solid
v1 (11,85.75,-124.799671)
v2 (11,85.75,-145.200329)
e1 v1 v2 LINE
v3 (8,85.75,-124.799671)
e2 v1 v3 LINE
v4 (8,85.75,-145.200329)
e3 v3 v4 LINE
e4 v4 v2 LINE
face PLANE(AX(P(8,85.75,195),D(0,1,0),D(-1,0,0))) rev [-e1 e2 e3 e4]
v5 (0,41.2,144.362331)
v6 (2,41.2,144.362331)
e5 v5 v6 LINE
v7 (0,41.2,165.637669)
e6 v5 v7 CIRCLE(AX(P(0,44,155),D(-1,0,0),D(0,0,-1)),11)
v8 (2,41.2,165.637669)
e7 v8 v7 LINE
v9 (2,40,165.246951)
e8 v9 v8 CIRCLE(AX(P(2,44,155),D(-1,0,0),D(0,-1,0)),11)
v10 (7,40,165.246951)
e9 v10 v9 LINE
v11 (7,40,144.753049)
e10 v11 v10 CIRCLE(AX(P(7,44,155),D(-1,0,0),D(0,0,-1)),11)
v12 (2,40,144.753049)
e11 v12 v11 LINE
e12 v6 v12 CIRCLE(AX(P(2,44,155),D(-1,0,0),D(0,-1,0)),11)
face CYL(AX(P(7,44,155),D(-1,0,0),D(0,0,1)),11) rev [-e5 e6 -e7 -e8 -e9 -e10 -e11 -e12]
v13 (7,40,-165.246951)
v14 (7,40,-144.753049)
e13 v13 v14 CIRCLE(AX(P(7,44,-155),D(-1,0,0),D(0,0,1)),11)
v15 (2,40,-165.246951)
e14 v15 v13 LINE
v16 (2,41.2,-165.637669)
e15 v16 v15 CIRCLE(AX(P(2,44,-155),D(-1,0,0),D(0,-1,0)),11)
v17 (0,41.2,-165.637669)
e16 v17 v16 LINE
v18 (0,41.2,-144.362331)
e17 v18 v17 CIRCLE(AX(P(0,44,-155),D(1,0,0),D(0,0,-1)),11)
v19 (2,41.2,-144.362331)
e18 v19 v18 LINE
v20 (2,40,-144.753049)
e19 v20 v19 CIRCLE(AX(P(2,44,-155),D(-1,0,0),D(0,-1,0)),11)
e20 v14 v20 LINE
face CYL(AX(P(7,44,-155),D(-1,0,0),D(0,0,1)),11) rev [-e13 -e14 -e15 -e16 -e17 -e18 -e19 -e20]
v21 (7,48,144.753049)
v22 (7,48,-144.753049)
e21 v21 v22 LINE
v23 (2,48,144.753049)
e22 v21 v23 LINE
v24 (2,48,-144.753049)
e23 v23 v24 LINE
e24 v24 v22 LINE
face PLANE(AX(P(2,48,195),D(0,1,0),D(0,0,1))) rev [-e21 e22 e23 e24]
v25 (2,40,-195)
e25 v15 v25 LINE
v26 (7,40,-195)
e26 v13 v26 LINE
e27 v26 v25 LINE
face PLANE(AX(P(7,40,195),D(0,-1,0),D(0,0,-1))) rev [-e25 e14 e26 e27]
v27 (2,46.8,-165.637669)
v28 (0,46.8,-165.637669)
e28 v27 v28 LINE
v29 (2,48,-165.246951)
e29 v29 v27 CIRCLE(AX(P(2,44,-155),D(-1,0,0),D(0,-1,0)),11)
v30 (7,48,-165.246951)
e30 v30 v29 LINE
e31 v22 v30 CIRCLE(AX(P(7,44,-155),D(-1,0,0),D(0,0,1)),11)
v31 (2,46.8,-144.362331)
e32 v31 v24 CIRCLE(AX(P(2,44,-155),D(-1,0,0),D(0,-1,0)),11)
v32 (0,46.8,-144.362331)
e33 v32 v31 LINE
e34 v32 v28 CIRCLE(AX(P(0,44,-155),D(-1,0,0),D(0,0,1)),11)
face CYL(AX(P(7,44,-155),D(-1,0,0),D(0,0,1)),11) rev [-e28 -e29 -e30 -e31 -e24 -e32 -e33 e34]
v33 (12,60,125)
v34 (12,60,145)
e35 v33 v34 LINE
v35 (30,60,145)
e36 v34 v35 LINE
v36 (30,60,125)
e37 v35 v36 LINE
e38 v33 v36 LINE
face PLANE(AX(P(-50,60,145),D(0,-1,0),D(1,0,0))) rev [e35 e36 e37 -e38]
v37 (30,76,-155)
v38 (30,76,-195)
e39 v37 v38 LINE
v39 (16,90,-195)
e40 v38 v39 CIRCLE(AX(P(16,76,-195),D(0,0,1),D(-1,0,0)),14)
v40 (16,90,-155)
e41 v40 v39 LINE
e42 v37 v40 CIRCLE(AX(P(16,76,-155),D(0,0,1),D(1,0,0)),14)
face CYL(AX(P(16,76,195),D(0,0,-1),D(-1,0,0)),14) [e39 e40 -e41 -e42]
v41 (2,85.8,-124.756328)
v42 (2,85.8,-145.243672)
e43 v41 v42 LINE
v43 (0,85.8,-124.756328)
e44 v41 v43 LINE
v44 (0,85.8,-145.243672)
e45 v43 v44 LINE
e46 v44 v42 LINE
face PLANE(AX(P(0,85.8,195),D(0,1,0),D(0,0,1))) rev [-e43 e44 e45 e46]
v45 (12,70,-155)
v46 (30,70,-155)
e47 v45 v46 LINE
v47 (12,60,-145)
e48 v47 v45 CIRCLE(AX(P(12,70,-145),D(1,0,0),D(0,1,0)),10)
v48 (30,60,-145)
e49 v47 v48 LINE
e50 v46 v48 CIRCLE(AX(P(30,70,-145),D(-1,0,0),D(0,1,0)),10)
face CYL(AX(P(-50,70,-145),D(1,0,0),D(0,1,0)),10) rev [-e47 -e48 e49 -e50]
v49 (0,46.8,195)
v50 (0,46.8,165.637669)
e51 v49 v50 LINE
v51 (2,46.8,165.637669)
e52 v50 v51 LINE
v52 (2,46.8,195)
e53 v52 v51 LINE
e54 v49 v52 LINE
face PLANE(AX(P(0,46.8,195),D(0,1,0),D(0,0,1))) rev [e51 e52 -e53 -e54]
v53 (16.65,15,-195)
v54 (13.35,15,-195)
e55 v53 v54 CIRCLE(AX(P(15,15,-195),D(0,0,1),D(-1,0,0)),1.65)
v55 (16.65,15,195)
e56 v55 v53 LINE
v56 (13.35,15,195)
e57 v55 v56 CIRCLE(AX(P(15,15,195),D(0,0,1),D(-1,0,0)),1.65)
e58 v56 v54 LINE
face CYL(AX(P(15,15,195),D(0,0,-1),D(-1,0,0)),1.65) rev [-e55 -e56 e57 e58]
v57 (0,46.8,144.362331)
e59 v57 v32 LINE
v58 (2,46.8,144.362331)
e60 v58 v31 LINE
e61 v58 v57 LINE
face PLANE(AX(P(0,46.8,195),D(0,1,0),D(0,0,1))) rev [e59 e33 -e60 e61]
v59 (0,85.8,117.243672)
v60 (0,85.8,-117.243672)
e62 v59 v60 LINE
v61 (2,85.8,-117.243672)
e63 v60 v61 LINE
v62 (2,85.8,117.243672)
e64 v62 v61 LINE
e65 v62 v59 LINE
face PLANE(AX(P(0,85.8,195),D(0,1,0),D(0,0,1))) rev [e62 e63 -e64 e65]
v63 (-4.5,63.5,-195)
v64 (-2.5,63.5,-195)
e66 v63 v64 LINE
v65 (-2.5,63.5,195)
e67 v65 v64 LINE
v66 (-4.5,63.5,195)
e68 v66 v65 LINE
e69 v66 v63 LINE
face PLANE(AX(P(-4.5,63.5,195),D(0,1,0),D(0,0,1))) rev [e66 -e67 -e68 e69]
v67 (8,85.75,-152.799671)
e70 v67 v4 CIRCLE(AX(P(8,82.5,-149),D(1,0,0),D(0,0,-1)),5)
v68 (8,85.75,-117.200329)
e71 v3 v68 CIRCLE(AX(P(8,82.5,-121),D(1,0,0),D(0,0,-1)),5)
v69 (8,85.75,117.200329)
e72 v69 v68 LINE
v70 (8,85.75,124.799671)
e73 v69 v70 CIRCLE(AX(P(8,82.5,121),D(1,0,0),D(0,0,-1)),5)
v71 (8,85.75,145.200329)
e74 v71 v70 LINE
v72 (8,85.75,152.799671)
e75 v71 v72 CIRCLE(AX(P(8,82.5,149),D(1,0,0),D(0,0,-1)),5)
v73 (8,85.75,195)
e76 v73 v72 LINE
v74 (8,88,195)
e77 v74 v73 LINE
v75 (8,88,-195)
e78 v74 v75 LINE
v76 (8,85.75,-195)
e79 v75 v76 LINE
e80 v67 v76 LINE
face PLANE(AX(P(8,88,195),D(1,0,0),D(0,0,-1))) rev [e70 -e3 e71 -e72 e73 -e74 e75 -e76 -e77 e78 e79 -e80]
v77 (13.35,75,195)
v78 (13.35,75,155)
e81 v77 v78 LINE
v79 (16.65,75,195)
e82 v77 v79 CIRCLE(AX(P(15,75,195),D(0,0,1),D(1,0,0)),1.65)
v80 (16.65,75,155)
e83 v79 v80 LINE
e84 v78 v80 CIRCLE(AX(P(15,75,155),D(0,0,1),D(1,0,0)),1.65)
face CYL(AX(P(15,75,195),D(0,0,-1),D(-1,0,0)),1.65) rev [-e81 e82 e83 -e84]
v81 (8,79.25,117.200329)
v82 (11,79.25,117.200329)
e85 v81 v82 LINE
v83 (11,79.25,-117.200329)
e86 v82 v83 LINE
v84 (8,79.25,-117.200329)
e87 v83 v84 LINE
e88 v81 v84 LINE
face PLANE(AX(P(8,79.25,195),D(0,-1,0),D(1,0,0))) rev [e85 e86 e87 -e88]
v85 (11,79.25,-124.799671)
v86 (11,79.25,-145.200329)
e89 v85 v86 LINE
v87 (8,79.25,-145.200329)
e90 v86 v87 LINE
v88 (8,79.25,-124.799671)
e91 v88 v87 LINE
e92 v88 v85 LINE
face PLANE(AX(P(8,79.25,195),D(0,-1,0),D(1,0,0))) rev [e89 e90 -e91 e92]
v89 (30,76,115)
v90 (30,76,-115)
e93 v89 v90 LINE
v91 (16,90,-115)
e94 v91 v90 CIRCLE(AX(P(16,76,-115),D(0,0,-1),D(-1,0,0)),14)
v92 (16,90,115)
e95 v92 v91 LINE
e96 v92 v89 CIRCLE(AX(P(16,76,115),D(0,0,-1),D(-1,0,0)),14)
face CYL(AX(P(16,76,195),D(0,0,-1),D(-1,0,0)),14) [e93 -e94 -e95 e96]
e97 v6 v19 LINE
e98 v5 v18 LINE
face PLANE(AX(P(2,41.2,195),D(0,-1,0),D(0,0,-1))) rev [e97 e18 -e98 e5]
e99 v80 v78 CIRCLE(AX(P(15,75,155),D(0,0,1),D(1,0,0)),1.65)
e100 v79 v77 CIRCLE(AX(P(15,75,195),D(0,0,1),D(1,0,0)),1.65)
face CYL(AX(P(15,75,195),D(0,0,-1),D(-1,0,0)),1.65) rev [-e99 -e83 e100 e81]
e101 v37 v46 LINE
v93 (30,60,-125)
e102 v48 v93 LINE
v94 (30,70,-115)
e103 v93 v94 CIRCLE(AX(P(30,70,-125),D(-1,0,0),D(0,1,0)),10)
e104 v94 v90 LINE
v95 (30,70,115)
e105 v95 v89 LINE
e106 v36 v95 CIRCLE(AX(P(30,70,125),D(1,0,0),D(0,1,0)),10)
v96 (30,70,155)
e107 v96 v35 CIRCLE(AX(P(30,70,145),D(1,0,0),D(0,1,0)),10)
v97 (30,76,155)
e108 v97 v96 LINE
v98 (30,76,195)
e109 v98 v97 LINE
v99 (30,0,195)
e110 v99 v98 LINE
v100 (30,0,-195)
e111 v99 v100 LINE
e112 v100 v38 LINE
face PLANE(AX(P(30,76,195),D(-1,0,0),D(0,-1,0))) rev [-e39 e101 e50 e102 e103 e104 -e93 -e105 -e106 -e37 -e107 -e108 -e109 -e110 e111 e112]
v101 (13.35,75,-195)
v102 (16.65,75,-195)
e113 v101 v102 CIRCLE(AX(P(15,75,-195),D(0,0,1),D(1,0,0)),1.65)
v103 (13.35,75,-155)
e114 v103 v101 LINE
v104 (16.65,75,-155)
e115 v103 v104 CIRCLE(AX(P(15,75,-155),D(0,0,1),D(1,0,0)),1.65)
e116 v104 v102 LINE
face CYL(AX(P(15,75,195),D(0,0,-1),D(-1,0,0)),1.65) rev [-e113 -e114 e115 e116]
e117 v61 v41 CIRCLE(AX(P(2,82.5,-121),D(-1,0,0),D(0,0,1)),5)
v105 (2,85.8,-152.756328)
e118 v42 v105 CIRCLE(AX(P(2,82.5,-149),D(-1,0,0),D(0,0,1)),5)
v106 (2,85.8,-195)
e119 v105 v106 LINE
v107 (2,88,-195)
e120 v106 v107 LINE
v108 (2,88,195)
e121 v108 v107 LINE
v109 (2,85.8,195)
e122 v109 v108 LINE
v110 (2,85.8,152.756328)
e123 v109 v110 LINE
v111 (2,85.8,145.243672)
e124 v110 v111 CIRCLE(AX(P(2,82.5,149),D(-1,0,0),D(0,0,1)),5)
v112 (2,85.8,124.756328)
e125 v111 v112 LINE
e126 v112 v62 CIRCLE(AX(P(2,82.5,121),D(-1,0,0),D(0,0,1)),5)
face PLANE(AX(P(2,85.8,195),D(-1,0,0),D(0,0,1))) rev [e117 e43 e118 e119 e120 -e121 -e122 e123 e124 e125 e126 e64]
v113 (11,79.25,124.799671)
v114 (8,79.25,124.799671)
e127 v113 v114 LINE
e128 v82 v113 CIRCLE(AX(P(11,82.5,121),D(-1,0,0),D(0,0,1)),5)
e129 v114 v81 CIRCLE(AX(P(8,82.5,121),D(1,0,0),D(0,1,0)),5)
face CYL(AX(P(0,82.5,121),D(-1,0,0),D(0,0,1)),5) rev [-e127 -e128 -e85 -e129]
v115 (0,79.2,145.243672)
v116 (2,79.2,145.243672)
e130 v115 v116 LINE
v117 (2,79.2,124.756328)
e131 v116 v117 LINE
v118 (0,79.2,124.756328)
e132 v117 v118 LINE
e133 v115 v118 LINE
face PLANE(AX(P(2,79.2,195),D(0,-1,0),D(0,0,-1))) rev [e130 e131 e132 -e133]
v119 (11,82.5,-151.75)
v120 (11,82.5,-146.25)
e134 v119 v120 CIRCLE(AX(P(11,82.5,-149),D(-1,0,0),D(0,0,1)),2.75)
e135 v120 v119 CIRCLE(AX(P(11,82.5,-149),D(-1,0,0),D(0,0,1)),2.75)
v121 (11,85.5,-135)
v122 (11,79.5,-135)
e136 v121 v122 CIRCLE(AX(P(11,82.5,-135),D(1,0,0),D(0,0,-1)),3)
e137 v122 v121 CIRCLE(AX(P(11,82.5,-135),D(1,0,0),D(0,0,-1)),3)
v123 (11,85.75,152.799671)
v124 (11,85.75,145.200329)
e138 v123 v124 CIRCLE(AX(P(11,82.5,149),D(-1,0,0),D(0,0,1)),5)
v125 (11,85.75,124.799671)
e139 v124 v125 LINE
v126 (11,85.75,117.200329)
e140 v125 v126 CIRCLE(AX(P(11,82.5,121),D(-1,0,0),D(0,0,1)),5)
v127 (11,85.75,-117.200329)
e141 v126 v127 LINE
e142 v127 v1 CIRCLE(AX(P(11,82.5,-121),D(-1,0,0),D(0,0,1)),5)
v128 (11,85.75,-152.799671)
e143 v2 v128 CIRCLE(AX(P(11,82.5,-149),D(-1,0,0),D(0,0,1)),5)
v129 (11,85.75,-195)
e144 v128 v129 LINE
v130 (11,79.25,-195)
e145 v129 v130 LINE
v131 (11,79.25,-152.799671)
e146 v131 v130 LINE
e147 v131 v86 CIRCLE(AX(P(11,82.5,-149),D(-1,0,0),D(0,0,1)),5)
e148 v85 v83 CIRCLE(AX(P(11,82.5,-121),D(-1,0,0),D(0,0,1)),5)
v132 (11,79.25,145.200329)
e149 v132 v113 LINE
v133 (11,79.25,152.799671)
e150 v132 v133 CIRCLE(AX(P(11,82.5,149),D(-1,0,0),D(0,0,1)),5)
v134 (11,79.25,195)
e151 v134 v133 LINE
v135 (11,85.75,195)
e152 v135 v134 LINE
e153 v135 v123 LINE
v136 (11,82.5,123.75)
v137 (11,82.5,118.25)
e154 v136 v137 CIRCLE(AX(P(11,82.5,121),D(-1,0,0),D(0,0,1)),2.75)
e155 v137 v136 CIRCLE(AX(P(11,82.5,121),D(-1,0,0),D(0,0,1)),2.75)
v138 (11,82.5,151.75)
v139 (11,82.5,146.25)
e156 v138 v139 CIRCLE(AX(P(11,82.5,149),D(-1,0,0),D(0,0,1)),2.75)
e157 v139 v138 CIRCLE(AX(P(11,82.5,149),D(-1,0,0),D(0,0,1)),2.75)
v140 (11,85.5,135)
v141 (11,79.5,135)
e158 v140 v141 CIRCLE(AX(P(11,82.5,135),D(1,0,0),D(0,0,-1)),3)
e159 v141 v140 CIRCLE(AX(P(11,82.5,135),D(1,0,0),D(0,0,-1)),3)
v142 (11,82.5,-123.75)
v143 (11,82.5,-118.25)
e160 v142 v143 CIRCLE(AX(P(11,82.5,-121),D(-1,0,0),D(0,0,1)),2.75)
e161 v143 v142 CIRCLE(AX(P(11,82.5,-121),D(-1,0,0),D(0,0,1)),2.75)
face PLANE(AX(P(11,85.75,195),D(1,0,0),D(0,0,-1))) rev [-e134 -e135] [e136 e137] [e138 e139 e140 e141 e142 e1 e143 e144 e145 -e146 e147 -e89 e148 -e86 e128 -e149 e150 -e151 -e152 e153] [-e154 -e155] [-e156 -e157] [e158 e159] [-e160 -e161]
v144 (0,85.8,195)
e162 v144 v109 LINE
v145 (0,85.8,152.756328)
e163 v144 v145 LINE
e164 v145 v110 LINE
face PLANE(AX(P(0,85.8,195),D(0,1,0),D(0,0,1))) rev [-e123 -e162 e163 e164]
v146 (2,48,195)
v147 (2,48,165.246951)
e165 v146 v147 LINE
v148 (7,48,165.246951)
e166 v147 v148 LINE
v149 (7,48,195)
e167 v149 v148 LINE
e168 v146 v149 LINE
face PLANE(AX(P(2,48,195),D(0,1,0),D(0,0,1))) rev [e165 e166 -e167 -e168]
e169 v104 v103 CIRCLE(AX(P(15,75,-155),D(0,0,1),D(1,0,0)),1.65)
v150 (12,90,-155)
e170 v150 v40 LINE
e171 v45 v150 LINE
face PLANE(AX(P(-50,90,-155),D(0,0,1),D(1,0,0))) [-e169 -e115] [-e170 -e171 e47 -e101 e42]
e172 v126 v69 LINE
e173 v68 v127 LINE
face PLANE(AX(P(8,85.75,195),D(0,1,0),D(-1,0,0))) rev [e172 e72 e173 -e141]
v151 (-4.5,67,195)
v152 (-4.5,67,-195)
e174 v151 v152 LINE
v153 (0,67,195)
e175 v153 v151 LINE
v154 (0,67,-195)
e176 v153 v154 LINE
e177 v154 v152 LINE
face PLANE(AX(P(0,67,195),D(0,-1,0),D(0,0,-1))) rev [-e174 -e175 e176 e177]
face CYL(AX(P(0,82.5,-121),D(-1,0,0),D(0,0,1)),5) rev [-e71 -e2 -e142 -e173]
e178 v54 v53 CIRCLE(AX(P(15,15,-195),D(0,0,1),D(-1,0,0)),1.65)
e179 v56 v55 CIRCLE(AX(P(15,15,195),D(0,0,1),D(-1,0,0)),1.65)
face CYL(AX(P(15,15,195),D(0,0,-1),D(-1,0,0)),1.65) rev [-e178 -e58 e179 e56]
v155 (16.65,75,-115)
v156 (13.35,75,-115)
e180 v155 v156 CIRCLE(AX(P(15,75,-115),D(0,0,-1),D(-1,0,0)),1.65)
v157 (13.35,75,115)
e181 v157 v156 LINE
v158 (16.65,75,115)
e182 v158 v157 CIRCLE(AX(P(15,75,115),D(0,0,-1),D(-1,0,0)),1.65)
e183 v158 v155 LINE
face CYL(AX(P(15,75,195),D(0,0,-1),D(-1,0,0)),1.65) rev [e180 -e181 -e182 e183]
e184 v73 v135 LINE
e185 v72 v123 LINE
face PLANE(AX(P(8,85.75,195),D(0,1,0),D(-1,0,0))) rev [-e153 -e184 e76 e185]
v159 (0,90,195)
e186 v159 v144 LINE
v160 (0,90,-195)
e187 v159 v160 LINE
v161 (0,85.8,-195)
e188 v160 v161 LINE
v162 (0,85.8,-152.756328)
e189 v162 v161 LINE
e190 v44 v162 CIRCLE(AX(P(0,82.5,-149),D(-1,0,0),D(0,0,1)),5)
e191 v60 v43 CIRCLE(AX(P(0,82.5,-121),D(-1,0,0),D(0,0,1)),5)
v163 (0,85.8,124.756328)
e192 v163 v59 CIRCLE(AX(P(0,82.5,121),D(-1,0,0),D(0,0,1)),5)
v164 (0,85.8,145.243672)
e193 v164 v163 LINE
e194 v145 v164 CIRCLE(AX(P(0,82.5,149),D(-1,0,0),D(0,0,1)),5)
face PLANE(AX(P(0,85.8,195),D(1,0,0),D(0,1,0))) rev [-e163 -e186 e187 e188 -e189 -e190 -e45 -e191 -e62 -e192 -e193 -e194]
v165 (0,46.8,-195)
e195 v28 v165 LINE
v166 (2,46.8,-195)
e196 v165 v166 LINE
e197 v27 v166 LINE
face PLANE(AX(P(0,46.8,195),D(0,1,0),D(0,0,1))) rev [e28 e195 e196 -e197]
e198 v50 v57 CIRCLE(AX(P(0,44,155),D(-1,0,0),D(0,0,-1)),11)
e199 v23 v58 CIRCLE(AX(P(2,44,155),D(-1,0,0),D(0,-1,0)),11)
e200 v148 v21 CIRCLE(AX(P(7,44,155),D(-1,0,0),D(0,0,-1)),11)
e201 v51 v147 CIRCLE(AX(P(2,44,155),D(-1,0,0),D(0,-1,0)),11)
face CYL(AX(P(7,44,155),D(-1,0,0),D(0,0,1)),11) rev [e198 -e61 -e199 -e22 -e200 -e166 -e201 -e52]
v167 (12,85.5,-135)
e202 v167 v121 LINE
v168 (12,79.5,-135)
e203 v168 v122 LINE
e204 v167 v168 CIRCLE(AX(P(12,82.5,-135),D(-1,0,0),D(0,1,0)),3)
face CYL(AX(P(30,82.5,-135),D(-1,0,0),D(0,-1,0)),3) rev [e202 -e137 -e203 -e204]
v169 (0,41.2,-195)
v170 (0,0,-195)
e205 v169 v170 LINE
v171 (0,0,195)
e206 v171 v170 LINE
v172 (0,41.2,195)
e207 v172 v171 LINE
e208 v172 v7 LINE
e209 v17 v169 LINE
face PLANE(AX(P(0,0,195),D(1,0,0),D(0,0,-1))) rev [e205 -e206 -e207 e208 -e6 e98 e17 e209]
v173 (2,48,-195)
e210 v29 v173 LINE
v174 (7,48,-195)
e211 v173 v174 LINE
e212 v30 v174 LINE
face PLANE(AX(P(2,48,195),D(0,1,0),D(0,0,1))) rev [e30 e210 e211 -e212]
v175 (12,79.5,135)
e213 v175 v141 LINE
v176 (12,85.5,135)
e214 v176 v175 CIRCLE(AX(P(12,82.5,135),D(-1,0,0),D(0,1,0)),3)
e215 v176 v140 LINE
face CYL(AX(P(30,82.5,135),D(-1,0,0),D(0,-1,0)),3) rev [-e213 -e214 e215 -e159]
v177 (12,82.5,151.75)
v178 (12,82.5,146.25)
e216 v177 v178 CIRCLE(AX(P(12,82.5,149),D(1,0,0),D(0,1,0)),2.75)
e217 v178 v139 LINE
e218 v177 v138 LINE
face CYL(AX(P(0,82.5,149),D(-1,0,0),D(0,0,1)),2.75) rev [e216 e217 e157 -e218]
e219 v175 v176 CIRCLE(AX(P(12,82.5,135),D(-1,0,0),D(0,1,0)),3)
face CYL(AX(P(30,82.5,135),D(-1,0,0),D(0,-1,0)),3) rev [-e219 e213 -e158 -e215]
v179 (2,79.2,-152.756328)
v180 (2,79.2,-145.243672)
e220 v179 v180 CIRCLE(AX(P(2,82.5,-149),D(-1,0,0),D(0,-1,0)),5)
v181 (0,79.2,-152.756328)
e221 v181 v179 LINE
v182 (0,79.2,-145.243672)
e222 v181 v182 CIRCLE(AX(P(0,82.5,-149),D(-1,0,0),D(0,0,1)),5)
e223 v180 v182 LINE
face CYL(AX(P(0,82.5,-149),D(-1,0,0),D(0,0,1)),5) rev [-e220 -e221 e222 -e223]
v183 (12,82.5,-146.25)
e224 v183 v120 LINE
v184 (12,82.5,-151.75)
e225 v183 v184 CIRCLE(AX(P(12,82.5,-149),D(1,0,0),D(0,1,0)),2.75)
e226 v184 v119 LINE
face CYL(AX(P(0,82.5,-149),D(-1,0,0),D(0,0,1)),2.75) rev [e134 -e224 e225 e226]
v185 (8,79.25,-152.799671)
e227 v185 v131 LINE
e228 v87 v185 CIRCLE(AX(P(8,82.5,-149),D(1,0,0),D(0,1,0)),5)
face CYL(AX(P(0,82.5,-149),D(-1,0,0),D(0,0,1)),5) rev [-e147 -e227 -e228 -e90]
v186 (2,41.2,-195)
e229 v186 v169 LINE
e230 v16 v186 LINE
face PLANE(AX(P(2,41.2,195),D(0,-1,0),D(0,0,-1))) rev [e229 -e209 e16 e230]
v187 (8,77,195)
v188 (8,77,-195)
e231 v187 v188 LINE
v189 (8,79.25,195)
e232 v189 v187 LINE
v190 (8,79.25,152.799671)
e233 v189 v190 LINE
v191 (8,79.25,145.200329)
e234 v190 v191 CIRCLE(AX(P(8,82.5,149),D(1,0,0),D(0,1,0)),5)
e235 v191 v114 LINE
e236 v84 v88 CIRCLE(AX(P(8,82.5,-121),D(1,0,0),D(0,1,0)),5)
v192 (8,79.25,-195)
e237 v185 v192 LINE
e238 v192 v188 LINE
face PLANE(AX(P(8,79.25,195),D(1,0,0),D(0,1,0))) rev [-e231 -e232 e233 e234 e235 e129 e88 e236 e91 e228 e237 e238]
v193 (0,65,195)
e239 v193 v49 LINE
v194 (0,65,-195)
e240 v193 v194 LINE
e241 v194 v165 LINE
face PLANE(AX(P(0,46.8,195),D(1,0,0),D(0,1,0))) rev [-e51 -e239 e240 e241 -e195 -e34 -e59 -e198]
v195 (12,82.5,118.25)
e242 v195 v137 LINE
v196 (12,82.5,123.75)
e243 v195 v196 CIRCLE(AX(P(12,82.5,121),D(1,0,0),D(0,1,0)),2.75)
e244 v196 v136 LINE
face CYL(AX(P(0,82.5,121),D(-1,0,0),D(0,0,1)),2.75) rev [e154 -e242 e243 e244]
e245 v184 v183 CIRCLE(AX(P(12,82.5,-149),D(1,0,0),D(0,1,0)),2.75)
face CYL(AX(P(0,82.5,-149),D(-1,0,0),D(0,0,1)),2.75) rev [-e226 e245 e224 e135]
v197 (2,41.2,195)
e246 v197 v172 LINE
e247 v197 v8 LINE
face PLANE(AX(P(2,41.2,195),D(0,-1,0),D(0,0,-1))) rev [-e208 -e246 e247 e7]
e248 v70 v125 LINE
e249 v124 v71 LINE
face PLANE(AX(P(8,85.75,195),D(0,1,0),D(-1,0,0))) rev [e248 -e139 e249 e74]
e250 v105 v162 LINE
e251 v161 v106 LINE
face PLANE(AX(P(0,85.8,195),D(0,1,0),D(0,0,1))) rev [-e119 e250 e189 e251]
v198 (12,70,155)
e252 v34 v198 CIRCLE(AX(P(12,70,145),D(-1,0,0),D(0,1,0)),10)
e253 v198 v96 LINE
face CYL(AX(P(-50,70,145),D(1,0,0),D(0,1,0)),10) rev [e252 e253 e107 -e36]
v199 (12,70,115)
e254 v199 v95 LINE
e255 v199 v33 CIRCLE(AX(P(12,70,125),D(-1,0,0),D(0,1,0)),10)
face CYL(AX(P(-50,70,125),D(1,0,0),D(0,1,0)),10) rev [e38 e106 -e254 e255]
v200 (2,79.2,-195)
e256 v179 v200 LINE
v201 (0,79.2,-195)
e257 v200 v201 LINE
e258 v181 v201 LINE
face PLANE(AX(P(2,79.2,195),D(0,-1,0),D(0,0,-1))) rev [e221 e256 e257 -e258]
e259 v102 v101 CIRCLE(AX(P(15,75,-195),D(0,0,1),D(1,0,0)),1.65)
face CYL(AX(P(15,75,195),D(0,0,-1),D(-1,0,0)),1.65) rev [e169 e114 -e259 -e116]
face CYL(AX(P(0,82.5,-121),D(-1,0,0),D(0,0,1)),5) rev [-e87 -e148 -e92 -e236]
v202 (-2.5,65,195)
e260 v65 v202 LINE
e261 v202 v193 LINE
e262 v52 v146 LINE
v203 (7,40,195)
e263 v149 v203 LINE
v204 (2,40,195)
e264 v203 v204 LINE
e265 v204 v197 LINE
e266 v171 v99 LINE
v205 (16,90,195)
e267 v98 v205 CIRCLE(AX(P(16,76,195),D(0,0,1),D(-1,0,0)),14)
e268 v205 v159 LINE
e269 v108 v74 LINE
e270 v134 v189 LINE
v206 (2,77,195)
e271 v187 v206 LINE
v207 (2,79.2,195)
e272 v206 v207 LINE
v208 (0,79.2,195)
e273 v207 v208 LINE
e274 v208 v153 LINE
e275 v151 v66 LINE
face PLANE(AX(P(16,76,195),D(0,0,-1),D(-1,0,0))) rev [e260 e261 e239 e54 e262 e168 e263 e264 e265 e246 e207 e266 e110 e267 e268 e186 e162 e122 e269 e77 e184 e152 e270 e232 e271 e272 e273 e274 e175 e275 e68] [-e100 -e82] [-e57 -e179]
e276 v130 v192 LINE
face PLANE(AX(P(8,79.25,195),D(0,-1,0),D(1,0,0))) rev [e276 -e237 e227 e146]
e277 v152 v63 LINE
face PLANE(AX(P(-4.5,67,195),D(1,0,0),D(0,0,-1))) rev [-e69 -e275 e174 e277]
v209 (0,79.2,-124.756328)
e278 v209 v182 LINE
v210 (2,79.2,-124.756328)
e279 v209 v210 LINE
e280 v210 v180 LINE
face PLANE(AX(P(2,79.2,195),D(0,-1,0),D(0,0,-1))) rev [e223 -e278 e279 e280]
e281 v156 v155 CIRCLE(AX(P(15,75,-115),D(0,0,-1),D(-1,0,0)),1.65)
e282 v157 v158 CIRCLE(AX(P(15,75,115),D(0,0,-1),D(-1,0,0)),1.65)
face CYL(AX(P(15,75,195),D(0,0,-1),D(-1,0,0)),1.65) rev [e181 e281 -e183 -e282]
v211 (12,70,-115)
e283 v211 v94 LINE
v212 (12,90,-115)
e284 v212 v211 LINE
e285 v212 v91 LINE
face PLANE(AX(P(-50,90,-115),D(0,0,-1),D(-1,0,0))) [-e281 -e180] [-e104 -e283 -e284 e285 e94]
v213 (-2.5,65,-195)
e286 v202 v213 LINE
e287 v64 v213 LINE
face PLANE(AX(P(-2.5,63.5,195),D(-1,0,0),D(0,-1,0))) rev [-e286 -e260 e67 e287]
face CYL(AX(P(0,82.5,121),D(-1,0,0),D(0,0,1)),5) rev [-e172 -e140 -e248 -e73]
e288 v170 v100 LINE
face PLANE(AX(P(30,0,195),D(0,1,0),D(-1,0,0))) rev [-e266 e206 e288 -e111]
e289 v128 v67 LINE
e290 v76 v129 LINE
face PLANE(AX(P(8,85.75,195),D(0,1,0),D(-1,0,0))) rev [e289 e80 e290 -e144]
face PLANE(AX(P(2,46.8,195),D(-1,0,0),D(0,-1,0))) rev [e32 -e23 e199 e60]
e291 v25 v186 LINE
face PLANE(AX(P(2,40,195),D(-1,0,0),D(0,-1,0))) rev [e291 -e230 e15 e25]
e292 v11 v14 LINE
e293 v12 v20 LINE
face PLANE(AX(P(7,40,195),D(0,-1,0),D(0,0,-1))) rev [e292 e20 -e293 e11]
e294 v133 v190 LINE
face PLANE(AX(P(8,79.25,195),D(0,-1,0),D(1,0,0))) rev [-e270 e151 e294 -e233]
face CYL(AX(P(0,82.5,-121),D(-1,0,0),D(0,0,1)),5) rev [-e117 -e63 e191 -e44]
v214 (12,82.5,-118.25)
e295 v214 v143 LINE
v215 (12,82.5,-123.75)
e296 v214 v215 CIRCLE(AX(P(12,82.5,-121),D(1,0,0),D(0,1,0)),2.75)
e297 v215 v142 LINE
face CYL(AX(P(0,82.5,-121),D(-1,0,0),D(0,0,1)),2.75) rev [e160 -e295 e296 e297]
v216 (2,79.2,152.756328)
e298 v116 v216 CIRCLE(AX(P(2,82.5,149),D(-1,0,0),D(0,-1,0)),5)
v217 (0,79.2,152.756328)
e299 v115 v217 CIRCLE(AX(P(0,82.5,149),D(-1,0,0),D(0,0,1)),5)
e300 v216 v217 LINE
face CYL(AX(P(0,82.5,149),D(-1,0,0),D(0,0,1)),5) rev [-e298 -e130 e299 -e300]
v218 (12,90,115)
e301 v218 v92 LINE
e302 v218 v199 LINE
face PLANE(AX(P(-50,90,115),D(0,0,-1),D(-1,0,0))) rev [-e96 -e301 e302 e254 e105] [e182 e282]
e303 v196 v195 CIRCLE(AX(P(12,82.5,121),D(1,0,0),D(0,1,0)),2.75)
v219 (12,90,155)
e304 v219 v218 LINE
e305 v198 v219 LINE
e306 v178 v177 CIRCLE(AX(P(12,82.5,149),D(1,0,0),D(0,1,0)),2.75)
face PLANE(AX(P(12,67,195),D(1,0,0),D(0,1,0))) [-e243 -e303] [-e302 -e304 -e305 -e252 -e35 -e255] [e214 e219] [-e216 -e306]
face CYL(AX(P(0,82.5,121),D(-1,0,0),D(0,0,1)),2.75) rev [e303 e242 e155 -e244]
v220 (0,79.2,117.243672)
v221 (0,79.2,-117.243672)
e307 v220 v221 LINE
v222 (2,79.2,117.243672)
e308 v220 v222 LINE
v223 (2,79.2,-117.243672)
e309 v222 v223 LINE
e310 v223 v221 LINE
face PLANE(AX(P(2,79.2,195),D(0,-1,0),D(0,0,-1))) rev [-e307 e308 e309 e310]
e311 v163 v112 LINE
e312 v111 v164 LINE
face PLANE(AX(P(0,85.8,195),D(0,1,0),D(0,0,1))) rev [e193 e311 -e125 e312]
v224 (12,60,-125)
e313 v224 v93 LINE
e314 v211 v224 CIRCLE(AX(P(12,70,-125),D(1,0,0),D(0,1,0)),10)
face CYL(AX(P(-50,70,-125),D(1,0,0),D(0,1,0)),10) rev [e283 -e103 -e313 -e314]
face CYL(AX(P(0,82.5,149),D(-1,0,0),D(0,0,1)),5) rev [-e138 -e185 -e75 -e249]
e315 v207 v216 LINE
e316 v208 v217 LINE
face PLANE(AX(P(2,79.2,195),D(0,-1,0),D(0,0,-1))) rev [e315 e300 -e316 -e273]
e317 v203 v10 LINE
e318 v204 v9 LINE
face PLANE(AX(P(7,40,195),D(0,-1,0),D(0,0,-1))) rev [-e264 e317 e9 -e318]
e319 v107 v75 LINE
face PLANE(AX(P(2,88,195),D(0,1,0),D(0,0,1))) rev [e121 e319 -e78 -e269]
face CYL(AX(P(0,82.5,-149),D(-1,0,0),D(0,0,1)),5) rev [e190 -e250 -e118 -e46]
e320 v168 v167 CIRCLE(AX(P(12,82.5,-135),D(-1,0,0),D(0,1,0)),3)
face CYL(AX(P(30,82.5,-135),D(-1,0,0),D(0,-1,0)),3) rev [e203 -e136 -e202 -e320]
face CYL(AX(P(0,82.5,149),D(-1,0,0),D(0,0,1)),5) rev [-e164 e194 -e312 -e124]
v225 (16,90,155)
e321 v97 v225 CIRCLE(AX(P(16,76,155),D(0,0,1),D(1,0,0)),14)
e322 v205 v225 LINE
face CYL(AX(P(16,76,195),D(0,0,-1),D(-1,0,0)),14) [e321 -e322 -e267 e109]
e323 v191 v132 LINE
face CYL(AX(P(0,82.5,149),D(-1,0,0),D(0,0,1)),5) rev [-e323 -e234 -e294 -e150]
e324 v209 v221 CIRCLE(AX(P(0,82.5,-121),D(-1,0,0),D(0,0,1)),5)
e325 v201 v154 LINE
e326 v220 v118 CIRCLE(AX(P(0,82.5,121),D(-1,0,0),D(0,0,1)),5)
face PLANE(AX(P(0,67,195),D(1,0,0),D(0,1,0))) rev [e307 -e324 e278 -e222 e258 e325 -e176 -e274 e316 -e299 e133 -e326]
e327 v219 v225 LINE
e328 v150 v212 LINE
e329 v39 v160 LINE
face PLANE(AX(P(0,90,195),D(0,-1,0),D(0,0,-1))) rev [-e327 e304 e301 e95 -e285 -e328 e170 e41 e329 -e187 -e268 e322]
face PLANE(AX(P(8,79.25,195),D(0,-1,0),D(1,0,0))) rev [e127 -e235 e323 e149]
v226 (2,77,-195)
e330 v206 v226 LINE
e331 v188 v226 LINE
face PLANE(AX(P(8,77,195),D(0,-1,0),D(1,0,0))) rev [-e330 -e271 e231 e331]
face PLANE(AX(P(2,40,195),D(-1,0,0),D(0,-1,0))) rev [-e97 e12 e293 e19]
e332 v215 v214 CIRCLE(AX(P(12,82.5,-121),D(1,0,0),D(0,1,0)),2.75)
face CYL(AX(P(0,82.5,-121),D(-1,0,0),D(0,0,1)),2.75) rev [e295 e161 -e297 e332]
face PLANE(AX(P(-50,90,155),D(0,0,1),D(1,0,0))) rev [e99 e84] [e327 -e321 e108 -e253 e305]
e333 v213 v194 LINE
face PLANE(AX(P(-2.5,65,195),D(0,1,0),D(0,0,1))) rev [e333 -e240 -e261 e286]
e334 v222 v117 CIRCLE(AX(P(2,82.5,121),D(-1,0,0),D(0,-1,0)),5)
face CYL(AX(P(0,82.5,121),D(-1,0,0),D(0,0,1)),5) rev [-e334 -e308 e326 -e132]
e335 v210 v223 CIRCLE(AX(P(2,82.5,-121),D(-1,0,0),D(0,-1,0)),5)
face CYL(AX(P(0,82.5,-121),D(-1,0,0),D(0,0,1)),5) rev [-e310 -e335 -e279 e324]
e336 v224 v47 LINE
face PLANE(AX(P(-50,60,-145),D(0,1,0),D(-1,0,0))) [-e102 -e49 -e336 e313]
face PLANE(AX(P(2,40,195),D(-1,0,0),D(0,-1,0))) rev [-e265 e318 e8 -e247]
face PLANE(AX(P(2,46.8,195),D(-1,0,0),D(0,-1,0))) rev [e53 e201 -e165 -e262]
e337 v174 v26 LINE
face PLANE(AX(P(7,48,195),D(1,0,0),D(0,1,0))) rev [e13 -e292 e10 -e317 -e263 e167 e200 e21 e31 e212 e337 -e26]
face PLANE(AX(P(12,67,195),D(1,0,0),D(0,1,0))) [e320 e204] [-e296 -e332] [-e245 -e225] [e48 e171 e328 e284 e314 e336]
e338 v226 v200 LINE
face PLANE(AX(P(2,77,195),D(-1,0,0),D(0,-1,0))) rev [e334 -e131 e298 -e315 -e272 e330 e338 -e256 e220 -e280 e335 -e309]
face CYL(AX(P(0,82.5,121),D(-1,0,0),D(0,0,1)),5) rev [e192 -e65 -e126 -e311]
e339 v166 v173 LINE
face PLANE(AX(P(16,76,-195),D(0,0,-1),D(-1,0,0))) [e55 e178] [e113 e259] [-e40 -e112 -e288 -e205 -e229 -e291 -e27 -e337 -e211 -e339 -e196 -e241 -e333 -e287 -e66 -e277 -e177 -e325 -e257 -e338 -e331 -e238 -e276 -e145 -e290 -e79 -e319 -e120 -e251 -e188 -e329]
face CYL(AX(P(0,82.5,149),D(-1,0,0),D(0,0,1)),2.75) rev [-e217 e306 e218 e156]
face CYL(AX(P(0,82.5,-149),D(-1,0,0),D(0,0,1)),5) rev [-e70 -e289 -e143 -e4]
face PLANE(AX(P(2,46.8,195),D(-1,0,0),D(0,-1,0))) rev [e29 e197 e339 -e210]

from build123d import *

# Parameters (mm, degrees)
SKETCH1_R                                  = 1.65
BOSS_EXTRUDE1_DEPTH                        = 195
SKETCH2_R                                  = 11
CUT_EXTRUDE1_DEPTH                         = 7
SKETCH3_R                                  = 3
CUT_EXTRUDE2_DEPTH                         = 217.852484422
CUT_EXTRUDE4_DEPTH                         = 18
M5_SOCKET_HEAD_CAP_SCREW_TYPE1_D           = 5.5
M5_SOCKET_HEAD_CAP_SCREW_TYPE1_CBORE_D     = 10
M5_SOCKET_HEAD_CAP_SCREW_TYPE1_CBORE_DEPTH = 11


with BuildPart() as part:
    # Sketch1 → Boss-Extrude1 (new, symmetric)
    with BuildSketch(Plane.XY):
        with BuildLine():
            Line((0, 0), (0, 41.2))
            Line((0, 41.2), (2, 41.2))
            Line((2, 41.2), (2, 40))
            Line((2, 40), (7, 40))
            Line((7, 40), (7, 48))
            Line((7, 48), (2, 48))
            Line((2, 48), (2, 46.8))
            Line((2, 46.8), (0, 46.8))
            Line((0, 46.8), (0, 65))
            Line((0, 65), (-2.5, 65))
            Line((-2.5, 65), (-2.5, 63.5))
            Line((-2.5, 63.5), (-4.5, 63.5))
            Line((-4.5, 63.5), (-4.5, 67))
            Line((-4.5, 67), (0, 67))
            Line((0, 67), (0, 79.2))
            Line((0, 79.2), (2, 79.2))
            Line((2, 79.2), (2, 77))
            Line((2, 77), (8, 77))
            Line((8, 77), (8, 79.25))
            Line((8, 79.25), (11, 79.25))
            Line((11, 79.25), (11, 85.75))
            Line((11, 85.75), (8, 85.75))
            Line((8, 85.75), (8, 88))
            Line((8, 88), (2, 88))
            Line((2, 88), (2, 85.8))
            Line((2, 85.8), (0, 85.8))
            Line((0, 85.8), (0, 90))
            Line((0, 90), (16, 90))
            ThreePointArc((16, 90), (25.899494937, 85.899494937), (30, 76))
            Line((30, 76), (30, 0))
            Line((30, 0), (0, 0))
        make_face()
        with Locations((15, 75)):
            Circle(SKETCH1_R, mode=Mode.SUBTRACT)
        with Locations(Location((15, 15, 0), (0, 0, 180))):
            Circle(SKETCH1_R, mode=Mode.SUBTRACT)
    extrude(amount=BOSS_EXTRUDE1_DEPTH, both=True)

    # Sketch2 → Cut-Extrude1 (cut)
    with BuildSketch(Plane.ZY):
        with Locations((-155, 44)):
            Circle(SKETCH2_R)
        with Locations((155, 44)):
            Circle(SKETCH2_R)
    extrude(amount=-CUT_EXTRUDE1_DEPTH, mode=Mode.SUBTRACT)

    # Sketch3 → Cut-Extrude2 (cut, through all)
    with BuildSketch(Plane.ZY):
        with Locations(Location((-135, 82.5, 0), (0, 0, 270))):
            Circle(SKETCH3_R)
        with Locations(Location((135, 82.5, 0), (0, 0, 270))):
            Circle(SKETCH3_R)
    cut_extrude2 = extrude(amount=-CUT_EXTRUDE2_DEPTH, mode=Mode.SUBTRACT)

    # Sketch9 → Cut-Extrude4 (cut)
    with BuildSketch(Plane(origin=(30, 0, 0), x_dir=(0, 0, -1), z_dir=(1, 0, 0))):
        with BuildLine():
            Line((-155, 90), (-115, 90))
            Line((-115, 90), (-115, 70))
            ThreePointArc((-115, 70), (-117.928932188, 62.928932188), (-125, 60))
            Line((-125, 60), (-145, 60))
            ThreePointArc((-145, 60), (-152.071067812, 62.928932188), (-155, 70))
            Line((-155, 70), (-155, 90))
        make_face()
    cut_extrude4 = extrude(amount=-CUT_EXTRUDE4_DEPTH, mode=Mode.SUBTRACT)

    # M5 socket head cap screw type1 (through all)
    with Locations(Plane.ZY):
        with Locations((149, 82.5), (121, 82.5)):
            m5_socket_head_cap_screw_type1 = CounterBoreHole(M5_SOCKET_HEAD_CAP_SCREW_TYPE1_D / 2, M5_SOCKET_HEAD_CAP_SCREW_TYPE1_CBORE_D / 2, M5_SOCKET_HEAD_CAP_SCREW_TYPE1_CBORE_DEPTH)

    # Mirror2: Cut-Extrude2, Cut-Extrude4, M5 socket head cap screw type1 across plane
    add(cut_extrude2.mirror(Plane.XY), mode=Mode.SUBTRACT)
    add(cut_extrude4.mirror(Plane.XY), mode=Mode.SUBTRACT)
    add(m5_socket_head_cap_screw_type1.mirror(Plane.XY), mode=Mode.SUBTRACT)


solid = part.part
